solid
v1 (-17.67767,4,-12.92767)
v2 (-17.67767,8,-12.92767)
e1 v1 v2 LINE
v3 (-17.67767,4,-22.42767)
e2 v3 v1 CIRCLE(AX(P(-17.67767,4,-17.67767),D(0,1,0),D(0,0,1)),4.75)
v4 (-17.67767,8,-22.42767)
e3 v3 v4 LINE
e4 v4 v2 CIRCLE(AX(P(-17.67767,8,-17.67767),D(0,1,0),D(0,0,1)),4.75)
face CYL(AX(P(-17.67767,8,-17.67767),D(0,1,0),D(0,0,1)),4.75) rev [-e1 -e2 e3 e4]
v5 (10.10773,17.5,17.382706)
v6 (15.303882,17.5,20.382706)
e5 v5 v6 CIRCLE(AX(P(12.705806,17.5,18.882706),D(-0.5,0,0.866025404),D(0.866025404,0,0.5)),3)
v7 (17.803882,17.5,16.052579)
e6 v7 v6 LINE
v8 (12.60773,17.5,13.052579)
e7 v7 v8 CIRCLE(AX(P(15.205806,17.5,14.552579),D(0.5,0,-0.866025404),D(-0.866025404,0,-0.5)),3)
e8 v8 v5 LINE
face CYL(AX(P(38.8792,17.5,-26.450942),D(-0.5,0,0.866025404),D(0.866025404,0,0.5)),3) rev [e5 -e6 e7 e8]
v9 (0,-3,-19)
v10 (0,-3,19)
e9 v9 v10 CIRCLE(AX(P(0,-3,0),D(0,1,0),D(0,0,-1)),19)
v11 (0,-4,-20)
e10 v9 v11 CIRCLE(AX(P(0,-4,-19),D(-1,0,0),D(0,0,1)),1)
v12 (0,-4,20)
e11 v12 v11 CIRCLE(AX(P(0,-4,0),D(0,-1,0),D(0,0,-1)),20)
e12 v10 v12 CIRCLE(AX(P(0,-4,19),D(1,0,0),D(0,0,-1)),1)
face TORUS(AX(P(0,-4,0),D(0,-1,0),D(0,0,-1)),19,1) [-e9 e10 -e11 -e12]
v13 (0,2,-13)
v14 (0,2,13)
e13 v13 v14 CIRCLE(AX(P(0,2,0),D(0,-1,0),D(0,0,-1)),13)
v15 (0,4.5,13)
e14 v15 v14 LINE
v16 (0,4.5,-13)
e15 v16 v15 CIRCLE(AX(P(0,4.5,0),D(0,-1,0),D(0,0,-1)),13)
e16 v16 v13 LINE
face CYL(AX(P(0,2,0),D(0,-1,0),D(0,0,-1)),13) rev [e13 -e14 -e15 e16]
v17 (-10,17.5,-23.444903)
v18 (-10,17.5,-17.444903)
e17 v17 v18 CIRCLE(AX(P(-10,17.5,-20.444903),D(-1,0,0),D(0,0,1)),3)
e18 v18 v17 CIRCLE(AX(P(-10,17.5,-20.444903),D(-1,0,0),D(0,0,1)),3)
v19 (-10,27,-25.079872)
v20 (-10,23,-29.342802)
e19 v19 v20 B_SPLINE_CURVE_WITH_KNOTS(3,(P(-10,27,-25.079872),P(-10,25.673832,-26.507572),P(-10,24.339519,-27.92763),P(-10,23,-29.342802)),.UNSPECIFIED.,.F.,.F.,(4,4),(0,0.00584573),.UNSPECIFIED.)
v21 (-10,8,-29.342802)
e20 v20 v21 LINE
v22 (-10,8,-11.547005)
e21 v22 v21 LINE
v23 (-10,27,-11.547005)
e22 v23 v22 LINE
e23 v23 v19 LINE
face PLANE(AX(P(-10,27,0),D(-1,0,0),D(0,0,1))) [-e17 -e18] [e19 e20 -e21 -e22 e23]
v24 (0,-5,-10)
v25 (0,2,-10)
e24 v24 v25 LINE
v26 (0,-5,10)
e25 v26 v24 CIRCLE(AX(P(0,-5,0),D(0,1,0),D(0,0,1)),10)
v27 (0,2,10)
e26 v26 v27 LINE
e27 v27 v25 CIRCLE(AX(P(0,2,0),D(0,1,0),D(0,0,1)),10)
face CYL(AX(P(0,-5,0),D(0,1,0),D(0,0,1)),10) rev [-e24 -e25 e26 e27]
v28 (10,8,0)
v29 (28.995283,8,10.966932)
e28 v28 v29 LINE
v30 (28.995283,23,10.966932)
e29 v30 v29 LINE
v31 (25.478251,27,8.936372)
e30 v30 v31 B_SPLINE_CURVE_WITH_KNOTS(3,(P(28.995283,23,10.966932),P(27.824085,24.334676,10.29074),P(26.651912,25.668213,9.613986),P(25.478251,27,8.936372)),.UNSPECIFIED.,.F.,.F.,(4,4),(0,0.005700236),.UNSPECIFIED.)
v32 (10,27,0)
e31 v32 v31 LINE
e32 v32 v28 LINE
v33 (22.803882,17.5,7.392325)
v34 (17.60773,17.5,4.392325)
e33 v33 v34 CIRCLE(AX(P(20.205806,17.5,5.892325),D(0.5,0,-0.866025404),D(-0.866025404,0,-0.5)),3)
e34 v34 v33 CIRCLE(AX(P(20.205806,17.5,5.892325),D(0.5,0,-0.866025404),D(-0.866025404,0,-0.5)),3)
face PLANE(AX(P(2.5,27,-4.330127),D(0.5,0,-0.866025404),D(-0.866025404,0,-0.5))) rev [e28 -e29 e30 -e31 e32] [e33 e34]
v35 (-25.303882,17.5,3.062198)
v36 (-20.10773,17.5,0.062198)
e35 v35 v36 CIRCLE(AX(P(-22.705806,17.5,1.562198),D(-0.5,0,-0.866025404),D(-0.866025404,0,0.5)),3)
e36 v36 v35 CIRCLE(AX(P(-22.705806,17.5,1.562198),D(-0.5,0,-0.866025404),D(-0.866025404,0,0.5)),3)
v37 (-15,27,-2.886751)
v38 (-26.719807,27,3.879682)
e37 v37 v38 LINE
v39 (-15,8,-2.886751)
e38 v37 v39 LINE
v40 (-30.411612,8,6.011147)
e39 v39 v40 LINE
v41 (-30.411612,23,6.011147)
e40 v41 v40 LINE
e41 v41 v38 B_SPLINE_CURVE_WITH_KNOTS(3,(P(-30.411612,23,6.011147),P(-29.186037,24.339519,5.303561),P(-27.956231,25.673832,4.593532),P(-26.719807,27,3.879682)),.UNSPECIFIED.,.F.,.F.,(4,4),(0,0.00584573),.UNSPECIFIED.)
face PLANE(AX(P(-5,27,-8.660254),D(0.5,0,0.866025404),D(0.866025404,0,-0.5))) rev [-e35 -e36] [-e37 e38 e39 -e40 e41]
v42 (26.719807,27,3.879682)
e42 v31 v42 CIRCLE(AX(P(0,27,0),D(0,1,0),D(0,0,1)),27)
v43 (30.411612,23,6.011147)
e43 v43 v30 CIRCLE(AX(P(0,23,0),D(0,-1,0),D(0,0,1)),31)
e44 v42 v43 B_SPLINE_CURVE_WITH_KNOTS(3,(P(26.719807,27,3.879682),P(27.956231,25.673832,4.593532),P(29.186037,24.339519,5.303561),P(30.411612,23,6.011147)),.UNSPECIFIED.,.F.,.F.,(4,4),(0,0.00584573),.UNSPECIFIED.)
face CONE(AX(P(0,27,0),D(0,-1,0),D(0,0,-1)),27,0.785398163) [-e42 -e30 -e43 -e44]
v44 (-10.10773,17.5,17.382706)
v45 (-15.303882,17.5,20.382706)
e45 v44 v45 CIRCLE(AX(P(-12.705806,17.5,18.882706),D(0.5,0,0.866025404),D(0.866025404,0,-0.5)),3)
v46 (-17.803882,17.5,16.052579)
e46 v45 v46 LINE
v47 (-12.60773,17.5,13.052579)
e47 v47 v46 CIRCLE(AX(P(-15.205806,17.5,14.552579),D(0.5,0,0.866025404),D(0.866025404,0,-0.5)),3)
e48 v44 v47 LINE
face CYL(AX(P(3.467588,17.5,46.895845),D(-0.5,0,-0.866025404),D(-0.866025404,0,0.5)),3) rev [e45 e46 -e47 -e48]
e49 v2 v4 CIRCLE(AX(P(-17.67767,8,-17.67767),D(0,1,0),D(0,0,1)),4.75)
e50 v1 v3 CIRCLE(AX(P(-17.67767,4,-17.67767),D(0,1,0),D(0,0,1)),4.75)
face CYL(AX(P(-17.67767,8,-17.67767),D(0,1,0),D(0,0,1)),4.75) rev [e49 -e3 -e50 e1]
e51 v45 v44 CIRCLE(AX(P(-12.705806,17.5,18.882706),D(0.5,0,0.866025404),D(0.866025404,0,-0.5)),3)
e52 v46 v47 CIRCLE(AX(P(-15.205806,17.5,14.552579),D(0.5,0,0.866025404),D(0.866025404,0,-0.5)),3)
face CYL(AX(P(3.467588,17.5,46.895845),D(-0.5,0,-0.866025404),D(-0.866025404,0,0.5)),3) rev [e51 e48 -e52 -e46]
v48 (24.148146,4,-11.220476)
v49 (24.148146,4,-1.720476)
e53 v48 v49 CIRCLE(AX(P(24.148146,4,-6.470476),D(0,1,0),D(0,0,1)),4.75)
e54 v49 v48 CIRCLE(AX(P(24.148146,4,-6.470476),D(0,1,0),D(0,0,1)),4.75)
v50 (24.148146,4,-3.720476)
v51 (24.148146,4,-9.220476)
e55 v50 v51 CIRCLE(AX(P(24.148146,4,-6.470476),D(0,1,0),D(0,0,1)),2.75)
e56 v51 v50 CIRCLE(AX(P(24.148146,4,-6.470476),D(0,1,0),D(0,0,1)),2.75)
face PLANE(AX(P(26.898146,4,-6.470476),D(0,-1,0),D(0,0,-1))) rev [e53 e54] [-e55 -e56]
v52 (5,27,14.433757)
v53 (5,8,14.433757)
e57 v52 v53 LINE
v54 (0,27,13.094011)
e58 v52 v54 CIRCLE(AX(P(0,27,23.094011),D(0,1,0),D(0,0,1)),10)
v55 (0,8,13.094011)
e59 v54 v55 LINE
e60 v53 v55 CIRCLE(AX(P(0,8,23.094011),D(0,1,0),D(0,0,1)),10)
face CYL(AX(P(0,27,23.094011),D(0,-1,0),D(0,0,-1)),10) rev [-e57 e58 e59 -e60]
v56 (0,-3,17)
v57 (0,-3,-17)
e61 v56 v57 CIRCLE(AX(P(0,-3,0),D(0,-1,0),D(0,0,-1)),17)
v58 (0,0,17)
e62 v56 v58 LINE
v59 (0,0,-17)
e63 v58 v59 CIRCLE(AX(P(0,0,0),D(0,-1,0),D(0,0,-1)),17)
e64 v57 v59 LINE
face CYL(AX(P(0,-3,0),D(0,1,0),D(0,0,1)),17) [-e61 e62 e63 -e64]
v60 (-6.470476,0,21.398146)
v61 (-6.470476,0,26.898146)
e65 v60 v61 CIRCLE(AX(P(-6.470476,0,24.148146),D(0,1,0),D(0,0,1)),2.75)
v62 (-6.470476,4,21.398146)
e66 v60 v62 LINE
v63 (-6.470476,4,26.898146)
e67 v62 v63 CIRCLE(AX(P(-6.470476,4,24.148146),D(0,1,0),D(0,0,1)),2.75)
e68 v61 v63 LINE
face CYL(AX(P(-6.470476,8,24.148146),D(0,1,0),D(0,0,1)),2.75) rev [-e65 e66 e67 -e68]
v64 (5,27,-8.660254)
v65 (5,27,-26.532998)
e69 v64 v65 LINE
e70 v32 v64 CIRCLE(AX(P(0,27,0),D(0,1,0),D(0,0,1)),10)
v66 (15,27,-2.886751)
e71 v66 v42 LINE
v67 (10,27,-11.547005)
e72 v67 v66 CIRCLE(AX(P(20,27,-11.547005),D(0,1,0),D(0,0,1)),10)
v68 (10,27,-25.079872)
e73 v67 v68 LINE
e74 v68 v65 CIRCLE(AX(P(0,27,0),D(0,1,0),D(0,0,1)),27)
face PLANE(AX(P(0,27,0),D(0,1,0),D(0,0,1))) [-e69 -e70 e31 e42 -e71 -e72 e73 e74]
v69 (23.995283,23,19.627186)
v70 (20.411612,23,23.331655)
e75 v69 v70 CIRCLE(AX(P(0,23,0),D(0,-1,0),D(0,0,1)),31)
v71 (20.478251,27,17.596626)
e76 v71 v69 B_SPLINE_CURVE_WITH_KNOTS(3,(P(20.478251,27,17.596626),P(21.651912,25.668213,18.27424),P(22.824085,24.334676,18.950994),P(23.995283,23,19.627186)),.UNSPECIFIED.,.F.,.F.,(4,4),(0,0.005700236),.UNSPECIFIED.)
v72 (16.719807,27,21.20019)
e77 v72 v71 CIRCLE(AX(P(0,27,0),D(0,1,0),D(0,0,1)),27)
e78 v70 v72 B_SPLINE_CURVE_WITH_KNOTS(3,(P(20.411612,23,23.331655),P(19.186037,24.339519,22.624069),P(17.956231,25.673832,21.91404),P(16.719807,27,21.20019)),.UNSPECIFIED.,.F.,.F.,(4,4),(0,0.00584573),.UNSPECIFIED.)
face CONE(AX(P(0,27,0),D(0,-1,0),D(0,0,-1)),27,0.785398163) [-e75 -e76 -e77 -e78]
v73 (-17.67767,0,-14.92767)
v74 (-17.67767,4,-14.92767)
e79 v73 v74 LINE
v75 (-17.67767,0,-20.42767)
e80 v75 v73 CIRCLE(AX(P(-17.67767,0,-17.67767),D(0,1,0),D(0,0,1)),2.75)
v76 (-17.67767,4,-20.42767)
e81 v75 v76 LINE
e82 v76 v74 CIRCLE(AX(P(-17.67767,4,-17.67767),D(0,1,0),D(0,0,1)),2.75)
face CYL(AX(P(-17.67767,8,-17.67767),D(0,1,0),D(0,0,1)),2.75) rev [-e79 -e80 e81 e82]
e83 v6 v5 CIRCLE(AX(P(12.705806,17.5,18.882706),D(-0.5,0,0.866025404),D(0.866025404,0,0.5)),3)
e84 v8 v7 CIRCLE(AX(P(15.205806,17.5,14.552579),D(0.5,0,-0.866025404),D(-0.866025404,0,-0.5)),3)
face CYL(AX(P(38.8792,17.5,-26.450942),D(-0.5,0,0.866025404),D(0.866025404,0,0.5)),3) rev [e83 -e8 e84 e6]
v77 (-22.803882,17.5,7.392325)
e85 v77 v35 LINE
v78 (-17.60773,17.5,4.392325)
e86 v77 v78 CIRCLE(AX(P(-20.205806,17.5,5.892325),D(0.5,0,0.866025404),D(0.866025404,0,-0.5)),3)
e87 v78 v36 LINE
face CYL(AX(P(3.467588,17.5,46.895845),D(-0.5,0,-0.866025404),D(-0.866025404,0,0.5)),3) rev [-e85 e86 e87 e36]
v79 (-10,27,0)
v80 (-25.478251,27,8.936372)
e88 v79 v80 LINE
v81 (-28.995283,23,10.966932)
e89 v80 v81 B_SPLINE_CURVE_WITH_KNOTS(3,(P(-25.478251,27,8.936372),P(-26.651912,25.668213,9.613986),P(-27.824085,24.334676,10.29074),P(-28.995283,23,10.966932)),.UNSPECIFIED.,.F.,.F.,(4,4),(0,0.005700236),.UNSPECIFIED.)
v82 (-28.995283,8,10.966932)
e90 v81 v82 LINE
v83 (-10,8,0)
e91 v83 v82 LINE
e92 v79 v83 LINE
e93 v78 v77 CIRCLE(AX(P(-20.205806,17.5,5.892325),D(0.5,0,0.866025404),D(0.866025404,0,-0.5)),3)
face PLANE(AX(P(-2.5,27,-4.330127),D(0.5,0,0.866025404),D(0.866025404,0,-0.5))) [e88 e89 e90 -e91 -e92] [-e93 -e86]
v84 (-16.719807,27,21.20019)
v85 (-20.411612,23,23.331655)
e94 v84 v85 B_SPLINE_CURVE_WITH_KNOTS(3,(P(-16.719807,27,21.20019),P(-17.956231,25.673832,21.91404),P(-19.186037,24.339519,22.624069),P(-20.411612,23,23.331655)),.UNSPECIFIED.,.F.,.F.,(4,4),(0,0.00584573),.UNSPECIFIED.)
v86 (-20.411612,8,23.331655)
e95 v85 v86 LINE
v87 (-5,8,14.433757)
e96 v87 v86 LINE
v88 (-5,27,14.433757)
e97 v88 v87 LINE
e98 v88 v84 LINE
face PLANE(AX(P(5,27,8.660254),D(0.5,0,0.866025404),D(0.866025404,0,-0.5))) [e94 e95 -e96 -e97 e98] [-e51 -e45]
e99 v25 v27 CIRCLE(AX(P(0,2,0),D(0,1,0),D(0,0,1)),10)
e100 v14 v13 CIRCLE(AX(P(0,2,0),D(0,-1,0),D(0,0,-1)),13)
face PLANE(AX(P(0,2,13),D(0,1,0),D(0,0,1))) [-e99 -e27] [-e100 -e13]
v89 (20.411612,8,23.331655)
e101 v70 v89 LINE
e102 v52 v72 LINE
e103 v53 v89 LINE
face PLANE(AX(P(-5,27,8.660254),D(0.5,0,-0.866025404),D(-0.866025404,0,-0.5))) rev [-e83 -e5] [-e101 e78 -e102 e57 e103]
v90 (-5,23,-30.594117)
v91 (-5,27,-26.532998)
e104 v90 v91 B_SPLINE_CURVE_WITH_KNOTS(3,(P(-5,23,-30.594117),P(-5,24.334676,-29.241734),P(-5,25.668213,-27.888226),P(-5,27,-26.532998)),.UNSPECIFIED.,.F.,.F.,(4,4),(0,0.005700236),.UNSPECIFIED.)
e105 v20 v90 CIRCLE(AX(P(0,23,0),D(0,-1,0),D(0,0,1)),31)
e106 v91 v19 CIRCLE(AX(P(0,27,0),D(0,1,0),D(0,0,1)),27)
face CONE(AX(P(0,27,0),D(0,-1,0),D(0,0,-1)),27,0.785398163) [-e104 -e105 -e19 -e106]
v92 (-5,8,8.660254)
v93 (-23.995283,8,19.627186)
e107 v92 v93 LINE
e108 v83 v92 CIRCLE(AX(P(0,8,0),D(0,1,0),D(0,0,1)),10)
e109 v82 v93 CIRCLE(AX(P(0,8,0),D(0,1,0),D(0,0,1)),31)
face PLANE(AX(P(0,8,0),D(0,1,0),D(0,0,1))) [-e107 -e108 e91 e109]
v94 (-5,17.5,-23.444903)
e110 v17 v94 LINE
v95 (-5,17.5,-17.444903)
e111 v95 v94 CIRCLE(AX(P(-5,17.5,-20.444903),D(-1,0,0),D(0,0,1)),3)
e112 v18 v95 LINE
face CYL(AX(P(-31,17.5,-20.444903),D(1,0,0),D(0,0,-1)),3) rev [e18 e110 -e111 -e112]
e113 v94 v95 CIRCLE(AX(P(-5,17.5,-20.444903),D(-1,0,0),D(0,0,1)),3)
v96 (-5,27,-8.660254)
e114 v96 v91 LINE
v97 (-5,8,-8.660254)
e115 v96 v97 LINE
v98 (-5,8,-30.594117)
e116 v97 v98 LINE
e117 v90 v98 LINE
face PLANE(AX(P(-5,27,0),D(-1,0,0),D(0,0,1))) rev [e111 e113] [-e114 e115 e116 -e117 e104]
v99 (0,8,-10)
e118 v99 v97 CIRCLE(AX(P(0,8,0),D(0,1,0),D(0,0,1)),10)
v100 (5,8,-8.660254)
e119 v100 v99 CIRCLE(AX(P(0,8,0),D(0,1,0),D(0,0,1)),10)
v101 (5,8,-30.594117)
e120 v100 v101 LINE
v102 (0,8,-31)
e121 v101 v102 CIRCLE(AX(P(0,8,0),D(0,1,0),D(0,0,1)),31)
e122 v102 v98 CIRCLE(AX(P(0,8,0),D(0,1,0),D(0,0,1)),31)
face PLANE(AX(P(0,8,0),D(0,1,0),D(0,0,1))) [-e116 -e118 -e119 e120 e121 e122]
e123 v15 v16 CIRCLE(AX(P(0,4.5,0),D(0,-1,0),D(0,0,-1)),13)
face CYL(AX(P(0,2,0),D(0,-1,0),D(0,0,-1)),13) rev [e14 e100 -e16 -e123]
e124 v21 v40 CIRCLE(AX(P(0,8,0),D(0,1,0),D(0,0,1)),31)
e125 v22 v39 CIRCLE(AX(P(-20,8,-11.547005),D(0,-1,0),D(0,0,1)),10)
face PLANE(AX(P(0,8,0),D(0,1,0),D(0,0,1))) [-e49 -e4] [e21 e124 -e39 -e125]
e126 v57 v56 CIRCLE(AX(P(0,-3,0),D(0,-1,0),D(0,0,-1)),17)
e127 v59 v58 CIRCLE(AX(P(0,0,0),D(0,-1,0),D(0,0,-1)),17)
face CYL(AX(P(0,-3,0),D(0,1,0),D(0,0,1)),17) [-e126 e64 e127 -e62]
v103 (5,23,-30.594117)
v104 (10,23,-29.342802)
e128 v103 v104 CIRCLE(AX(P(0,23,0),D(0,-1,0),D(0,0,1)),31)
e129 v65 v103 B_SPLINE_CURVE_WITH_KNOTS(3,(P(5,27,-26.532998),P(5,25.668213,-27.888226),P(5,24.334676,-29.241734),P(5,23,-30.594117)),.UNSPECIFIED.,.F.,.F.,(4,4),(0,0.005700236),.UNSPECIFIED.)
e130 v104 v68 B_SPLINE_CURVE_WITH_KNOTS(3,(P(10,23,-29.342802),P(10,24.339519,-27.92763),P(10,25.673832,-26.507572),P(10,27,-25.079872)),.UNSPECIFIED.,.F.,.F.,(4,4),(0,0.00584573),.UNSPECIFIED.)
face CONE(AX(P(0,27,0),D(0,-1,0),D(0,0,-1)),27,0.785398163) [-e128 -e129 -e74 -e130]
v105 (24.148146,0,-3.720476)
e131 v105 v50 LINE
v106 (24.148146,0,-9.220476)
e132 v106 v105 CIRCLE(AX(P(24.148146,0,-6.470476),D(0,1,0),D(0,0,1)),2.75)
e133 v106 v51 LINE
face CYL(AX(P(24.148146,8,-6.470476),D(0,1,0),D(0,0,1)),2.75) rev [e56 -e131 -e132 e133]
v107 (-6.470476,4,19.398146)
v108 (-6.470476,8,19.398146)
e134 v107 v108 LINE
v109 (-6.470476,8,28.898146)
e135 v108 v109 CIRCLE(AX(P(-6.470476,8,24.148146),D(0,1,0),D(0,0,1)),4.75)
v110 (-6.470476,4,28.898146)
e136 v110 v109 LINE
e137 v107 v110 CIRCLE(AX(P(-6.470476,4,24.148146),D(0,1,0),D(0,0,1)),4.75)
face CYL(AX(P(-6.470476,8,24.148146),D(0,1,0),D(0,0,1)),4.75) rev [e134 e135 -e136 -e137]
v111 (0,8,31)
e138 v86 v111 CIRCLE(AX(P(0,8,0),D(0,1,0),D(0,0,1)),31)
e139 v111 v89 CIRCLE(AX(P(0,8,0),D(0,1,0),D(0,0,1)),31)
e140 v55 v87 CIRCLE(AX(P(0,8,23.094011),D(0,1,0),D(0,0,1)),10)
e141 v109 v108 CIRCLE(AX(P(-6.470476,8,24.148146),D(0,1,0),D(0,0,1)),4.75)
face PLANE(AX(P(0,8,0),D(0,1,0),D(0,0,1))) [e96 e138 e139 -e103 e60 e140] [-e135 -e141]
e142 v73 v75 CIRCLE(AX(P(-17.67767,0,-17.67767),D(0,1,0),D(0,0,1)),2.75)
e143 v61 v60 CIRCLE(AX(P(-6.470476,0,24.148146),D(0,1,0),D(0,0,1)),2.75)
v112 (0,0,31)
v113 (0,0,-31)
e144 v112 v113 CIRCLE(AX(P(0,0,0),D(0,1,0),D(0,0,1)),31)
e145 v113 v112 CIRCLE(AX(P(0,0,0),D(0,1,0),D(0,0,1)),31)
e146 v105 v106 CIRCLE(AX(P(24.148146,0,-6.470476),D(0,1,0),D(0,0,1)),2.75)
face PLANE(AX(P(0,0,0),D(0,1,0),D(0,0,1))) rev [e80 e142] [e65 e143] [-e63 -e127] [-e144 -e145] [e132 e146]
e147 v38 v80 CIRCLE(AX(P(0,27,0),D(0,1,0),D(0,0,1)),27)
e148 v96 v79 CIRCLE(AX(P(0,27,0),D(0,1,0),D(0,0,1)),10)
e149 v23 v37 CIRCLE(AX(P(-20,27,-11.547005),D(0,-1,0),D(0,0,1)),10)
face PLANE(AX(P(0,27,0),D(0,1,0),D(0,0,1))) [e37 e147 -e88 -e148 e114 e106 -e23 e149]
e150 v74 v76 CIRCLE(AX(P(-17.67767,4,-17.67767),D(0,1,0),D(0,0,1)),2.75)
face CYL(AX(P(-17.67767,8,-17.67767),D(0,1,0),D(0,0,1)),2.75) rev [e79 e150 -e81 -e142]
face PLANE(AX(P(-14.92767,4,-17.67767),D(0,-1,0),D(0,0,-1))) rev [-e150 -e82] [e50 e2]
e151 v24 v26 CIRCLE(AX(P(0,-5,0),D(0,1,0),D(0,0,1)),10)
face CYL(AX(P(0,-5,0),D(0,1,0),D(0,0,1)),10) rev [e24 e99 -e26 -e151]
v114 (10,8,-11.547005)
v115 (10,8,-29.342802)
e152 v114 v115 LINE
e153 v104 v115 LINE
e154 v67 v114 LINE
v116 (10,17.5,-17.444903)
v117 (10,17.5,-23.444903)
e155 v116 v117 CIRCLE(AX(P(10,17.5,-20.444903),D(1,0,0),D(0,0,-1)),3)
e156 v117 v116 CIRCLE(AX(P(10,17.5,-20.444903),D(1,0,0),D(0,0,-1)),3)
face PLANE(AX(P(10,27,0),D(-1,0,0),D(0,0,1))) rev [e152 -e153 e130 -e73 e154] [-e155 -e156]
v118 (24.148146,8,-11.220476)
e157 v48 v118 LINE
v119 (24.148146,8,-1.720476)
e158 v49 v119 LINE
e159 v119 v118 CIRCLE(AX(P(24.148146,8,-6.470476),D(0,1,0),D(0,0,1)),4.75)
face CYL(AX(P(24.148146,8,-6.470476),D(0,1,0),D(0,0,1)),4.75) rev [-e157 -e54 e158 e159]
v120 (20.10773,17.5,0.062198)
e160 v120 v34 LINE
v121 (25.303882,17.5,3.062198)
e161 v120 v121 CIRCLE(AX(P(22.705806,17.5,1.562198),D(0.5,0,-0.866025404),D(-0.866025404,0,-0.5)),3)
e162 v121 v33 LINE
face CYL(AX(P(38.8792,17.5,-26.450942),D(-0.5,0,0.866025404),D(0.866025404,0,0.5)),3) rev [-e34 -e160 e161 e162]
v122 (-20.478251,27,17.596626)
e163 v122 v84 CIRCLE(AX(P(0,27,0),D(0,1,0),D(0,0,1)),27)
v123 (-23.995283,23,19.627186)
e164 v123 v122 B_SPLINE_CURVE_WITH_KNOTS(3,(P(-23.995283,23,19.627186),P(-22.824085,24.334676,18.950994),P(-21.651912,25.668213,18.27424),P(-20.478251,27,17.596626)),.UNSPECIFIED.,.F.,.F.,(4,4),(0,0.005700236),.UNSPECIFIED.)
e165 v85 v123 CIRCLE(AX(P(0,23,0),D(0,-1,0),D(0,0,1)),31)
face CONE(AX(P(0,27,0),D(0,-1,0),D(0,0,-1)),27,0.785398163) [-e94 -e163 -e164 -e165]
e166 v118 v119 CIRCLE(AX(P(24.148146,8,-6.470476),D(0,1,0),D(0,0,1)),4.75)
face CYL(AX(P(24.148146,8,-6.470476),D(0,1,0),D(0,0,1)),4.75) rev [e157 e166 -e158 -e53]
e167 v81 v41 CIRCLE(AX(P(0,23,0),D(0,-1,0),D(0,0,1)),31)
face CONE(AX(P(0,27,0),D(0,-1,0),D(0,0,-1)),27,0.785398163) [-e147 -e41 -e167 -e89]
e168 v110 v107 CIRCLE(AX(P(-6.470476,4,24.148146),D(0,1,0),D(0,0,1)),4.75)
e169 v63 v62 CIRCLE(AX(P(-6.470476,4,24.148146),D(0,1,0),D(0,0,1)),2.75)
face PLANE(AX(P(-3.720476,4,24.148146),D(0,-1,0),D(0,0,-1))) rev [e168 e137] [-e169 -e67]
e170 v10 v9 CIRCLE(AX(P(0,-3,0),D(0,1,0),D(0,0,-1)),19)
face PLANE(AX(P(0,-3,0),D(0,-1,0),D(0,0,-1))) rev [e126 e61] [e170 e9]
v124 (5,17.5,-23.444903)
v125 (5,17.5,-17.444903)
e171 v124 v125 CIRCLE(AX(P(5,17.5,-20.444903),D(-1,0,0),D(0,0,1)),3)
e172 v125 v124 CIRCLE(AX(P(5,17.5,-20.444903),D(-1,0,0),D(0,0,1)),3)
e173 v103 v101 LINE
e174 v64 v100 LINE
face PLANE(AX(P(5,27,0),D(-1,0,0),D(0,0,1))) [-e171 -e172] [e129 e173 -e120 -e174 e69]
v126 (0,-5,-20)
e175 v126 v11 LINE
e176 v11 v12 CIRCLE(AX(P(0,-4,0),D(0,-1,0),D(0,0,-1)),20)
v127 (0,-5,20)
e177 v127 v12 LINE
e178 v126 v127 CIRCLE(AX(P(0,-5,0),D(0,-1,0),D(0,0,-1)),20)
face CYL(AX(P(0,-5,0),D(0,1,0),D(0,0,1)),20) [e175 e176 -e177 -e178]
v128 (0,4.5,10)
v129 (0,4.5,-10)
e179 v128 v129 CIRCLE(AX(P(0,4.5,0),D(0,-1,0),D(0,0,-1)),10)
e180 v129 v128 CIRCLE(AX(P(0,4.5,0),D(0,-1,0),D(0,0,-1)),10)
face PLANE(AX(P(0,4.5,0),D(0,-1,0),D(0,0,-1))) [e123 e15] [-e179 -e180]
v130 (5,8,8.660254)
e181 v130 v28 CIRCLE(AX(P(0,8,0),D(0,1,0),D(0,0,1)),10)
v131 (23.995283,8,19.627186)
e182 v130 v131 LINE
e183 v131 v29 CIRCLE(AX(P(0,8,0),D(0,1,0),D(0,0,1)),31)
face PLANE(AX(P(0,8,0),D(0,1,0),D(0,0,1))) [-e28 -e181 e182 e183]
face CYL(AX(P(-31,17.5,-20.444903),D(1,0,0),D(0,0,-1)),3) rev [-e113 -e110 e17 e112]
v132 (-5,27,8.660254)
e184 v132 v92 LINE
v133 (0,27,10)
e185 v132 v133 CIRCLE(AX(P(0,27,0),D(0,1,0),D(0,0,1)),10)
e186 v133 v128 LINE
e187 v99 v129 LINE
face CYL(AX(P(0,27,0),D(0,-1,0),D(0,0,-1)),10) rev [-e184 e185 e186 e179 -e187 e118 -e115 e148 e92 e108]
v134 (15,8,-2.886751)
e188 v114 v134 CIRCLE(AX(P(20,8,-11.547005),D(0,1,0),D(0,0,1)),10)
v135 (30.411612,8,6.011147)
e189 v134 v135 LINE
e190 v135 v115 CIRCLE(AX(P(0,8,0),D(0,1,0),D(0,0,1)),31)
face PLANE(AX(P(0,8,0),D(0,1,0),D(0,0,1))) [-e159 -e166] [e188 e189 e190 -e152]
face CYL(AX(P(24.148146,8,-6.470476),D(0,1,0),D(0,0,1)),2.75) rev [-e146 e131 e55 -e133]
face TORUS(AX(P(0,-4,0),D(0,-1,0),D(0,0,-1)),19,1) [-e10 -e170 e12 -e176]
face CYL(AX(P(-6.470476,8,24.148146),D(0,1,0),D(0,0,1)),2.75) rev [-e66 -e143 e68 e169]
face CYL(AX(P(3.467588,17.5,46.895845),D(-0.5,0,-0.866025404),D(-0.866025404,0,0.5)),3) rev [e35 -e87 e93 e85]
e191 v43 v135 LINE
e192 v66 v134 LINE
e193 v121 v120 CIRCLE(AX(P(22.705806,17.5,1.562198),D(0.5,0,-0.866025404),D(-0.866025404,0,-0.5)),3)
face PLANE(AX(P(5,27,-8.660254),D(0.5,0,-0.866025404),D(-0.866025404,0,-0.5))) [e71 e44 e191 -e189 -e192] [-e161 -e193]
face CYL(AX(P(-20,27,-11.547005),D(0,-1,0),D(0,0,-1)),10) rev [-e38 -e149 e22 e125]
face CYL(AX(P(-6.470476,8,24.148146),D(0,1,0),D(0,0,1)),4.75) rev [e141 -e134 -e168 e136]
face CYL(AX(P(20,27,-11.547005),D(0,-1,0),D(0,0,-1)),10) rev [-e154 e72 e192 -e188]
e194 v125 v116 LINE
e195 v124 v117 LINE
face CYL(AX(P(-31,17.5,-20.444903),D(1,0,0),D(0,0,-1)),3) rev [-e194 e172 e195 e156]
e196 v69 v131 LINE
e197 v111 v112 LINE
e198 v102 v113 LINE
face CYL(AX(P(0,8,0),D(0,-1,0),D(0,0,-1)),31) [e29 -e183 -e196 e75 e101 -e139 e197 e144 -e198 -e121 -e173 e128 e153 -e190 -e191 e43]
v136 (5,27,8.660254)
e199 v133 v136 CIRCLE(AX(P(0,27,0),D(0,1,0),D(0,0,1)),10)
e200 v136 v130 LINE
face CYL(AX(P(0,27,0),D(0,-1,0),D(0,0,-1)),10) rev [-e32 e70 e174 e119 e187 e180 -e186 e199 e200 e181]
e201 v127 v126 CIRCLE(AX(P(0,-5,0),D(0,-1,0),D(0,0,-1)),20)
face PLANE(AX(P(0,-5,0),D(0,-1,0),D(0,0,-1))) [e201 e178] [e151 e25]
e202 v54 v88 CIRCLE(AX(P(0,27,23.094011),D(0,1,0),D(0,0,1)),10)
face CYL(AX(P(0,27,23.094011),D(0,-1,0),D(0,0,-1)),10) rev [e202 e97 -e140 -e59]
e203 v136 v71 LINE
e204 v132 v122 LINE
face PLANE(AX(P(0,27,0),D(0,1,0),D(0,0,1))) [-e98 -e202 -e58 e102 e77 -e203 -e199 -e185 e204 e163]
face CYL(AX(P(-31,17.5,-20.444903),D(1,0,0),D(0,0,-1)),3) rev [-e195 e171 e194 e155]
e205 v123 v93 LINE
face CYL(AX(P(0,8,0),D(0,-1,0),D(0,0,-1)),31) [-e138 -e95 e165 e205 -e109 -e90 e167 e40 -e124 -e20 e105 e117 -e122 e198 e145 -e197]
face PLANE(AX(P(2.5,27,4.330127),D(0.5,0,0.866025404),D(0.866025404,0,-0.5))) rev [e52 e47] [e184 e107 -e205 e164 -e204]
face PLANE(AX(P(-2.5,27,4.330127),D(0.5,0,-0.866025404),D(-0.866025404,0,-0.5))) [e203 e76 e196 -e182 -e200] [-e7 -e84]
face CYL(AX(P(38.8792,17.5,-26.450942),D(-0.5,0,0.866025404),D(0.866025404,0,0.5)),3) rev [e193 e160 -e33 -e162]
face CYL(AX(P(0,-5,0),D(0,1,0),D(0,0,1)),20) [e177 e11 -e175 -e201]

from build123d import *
from build123d.topology import SkipClean

# Parameters (mm, degrees)
BASE_FLANGE_SKETCH_R                        = 31
BASE_FLANGE_62_DEPTH                        = 8
HUB_BOSS_SKETCH_R                           = 17
HUB_BOSS_34_DEPTH                           = 3
HUB_COLLAR_SKETCH_R                         = 20
HUB_COLLAR_40_DEPTH                         = 2
HUB_COLLAR_FILLET_R1_R                      = 1
CENTRAL_BORE_PROFILE_W                      = 13
CENTRAL_BORE_PROFILE_H                      = 2.5
MOUNTING_HOLES_3X_5_5_CBORE_9_5_D           = 5.5
MOUNTING_HOLES_3X_5_5_CBORE_9_5_DEPTH       = 8.774964387
MOUNTING_HOLES_3X_5_5_CBORE_9_5_CBORE_D     = 9.5
MOUNTING_HOLES_3X_5_5_CBORE_9_5_CBORE_DEPTH = 4
FORK_LUGS_DEPTH                             = 19
SKETCH8_6_R                                 = 10
FORK_LUG_RELIEF_CUT_DEPTH                   = 48.780749262
LUG_1_PIN_HOLE_SKETCH_R                     = 3
LUG_1_PIN_HOLE_6_DEPTH                      = 60.982795453
LUG_2_PIN_HOLE_SKETCH_R                     = 3
LUG_2_PIN_HOLE_6_DEPTH                      = 60.982795453
LUG_3_PIN_HOLE_SKETCH_R                     = 3
LUG_3_PIN_HOLE_6_DEPTH                      = 59.060313468
FORK_LUG_CHAMFER_4X45_SIZE                  = 4


with BuildPart() as part:
    # Base Flange Sketch → Base Flange _62 (new body)
    with BuildSketch(Plane(origin=(0, 0, 0), x_dir=(1, 0, 0), z_dir=(0, 1, 0))):
        with Locations(Location((0, 0, 0), (0, 0, 270))):
            Circle(BASE_FLANGE_SKETCH_R)
    extrude(amount=BASE_FLANGE_62_DEPTH)

    # Hub Boss Sketch → Hub Boss _34 (add)
    with BuildSketch(Plane.XZ):
        with Locations(Location((0, 0, 0), (0, 0, 270))):
            Circle(HUB_BOSS_SKETCH_R)
    extrude(amount=HUB_BOSS_34_DEPTH)

    # Hub Collar Sketch → Hub Collar _40 (add)
    with BuildSketch(Plane.XZ.offset(3)):
        with Locations(Location((0, 0, 0), (0, 0, 270))):
            Circle(HUB_COLLAR_SKETCH_R)
    extrude(amount=HUB_COLLAR_40_DEPTH)

    # Hub Collar Fillet R1
    hub_collar_fillet_r1_edges = [part.edges().sort_by_distance(p)[0] for p in [
        (0, -3, 20),
    ]]
    fillet(hub_collar_fillet_r1_edges, radius=HUB_COLLAR_FILLET_R1_R)

    # Central Bore Profile → Central Bore (revolve, cut)
    with BuildSketch(Plane(origin=(0, 0, 0), x_dir=(0, 0, -1), z_dir=(1, 0, 0)), mode=Mode.PRIVATE) as central_bore_sk:
        with Locations((-6.5, 3.25)):
            Rectangle(CENTRAL_BORE_PROFILE_W, CENTRAL_BORE_PROFILE_H)
    revolve(central_bore_sk.sketch.rotate(Axis((0, 2, 0), (0, 1, 0)), 180), axis=Axis((0, 2, 0), (0, 1, 0)), mode=Mode.SUBTRACT)

    # Mounting Holes 3x_5.5 CBore _9.5
    with Locations(Plane(origin=(0, 8, 0), x_dir=(1, 0, 0), z_dir=(0, 1, 0))):
        with Locations((-17.67766953, 17.67766953), (24.148145657, 6.470476128), (-6.470476128, -24.148145657)):
            CounterBoreHole(MOUNTING_HOLES_3X_5_5_CBORE_9_5_D / 2, MOUNTING_HOLES_3X_5_5_CBORE_9_5_CBORE_D / 2, MOUNTING_HOLES_3X_5_5_CBORE_9_5_CBORE_DEPTH, depth=MOUNTING_HOLES_3X_5_5_CBORE_9_5_DEPTH)

    # Fork Lugs Sketch → Fork Lugs (add)
    with BuildSketch(Plane(origin=(0, 8, 0), x_dir=(1, 0, 0), z_dir=(0, 1, 0))):
        with BuildLine():
            Line((5, 30.594117082), (5, 8.660254038))
            ThreePointArc((5, 8.660254038), (8.660254038, 5), (10, 0))
            Line((10, 0), (28.995282599, -10.966931522))
            ThreePointArc((28.995282599, -10.966931522), (29.806622049, -8.518525814), (30.411611519, -6.011146713))
            Line((30.411611519, -6.011146713), (15, 2.886751346))
            ThreePointArc((15, 2.886751346), (11.339745962, 6.547005384), (10, 11.547005384))
            Line((10, 11.547005384), (10, 29.342801502))
            ThreePointArc((10, 29.342801502), (7.526051267, 30.072554802), (5, 30.594117082))
        make_face()
        with BuildLine():
            ThreePointArc((-10, 0), (-8.660254038, 5), (-5, 8.660254038))
            Line((-5, 8.660254038), (-5, 30.594117082))
            ThreePointArc((-5, 30.594117082), (-7.526051267, 30.072554802), (-10, 29.342801502))
            Line((-10, 29.342801502), (-10, 11.547005384))
            ThreePointArc((-10, 11.547005384), (-11.339745962, 6.547005384), (-15, 2.886751346))
            Line((-15, 2.886751346), (-30.411611519, -6.011146713))
            ThreePointArc((-30.411611519, -6.011146713), (-29.806622049, -8.518525814), (-28.995282599, -10.966931522))
            Line((-28.995282599, -10.966931522), (-10, 0))
        make_face()
        with BuildLine():
            Line((23.995282599, -19.62718556), (5, -8.660254038))
            ThreePointArc((5, -8.660254038), (0, -10), (-5, -8.660254038))
            Line((-5, -8.660254038), (-23.995282599, -19.62718556))
            ThreePointArc((-23.995282599, -19.62718556), (-22.280570782, -21.554028988), (-20.411611519, -23.331654789))
            Line((-20.411611519, -23.331654789), (-5, -14.43375673))
            ThreePointArc((-5, -14.43375673), (0, -13.094010768), (5, -14.43375673))
            Line((5, -14.43375673), (20.411611519, -23.331654789))
            ThreePointArc((20.411611519, -23.331654789), (22.280570782, -21.554028988), (23.995282599, -19.62718556))
        make_face()
    extrude(amount=FORK_LUGS_DEPTH)

    # Sketch8_6 → Fork Lug Relief Cut (cut, through all)
    with SkipClean():  # the faces are left unmerged after this step: merging them gives an invalid solid
        with BuildSketch(Plane(origin=(0, 8, 0), x_dir=(1, 0, 0), z_dir=(0, 1, 0))):
            with Locations(Location((0, 0, 0), (0, 0, 90))):
                Circle(SKETCH8_6_R)
        extrude(amount=-FORK_LUG_RELIEF_CUT_DEPTH, mode=Mode.SUBTRACT)

    # Lug 1 Pin Hole Sketch → Lug 1 Pin Hole _6 (cut, through all)
    with SkipClean():  # the faces are left unmerged after this step: merging them gives an invalid solid
        with BuildSketch(Plane(origin=(-5, 0, 8.660254038), x_dir=(0.8660254037844363, 0, 0.5000000000000043), z_dir=(-0.5000000000000042, 0, 0.8660254037844362))):
            with Locations((20.444903443, 17.5)):
                Circle(LUG_1_PIN_HOLE_SKETCH_R)
        extrude(amount=-LUG_1_PIN_HOLE_6_DEPTH, mode=Mode.SUBTRACT)

    # Lug 2 Pin Hole Sketch → Lug 2 Pin Hole _6 (cut, through all)
    with SkipClean():  # the faces are left unmerged after this step: merging them gives an invalid solid
        with BuildSketch(Plane(origin=(-5, 0, -8.660254038), x_dir=(-0.8660254037844363, 0, 0.5000000000000042), z_dir=(-0.5000000000000042, 0, -0.8660254037844363))):
            with Locations(Location((20.444903443, 17.5, 0), (0, 0, 180))):
                Circle(LUG_2_PIN_HOLE_SKETCH_R)
        extrude(amount=-LUG_2_PIN_HOLE_6_DEPTH, mode=Mode.SUBTRACT)

    # Lug 3 Pin Hole Sketch → Lug 3 Pin Hole _6 (cut, through all)
    with SkipClean():  # the faces are left unmerged after this step: merging them gives an invalid solid
        with BuildSketch(Plane(origin=(10, 0, 0), x_dir=(0, 0, -1), z_dir=(1, 0, 0))):
            with Locations(Location((20.444903443, 17.5, 0), (0, 0, 180))):
                Circle(LUG_3_PIN_HOLE_SKETCH_R)
        extrude(amount=-LUG_3_PIN_HOLE_6_DEPTH, mode=Mode.SUBTRACT)

    # Fork Lug Chamfer 4x45
    fork_lug_chamfer_4x45_edges = [part.edges().sort_by_distance(p)[0] for p in [
        (7.526051267, 27, -30.072554802),
        (29.806622049, 27, 8.518525814),
        (-29.806622049, 27, 8.518525814),
        (-7.526051267, 27, -30.072554802),
        (22.280570782, 27, 21.554028988),
        (-22.280570782, 27, 21.554028988),
    ]]
    chamfer(fork_lug_chamfer_4x45_edges, length=FORK_LUG_CHAMFER_4X45_SIZE)


solid = part.part
